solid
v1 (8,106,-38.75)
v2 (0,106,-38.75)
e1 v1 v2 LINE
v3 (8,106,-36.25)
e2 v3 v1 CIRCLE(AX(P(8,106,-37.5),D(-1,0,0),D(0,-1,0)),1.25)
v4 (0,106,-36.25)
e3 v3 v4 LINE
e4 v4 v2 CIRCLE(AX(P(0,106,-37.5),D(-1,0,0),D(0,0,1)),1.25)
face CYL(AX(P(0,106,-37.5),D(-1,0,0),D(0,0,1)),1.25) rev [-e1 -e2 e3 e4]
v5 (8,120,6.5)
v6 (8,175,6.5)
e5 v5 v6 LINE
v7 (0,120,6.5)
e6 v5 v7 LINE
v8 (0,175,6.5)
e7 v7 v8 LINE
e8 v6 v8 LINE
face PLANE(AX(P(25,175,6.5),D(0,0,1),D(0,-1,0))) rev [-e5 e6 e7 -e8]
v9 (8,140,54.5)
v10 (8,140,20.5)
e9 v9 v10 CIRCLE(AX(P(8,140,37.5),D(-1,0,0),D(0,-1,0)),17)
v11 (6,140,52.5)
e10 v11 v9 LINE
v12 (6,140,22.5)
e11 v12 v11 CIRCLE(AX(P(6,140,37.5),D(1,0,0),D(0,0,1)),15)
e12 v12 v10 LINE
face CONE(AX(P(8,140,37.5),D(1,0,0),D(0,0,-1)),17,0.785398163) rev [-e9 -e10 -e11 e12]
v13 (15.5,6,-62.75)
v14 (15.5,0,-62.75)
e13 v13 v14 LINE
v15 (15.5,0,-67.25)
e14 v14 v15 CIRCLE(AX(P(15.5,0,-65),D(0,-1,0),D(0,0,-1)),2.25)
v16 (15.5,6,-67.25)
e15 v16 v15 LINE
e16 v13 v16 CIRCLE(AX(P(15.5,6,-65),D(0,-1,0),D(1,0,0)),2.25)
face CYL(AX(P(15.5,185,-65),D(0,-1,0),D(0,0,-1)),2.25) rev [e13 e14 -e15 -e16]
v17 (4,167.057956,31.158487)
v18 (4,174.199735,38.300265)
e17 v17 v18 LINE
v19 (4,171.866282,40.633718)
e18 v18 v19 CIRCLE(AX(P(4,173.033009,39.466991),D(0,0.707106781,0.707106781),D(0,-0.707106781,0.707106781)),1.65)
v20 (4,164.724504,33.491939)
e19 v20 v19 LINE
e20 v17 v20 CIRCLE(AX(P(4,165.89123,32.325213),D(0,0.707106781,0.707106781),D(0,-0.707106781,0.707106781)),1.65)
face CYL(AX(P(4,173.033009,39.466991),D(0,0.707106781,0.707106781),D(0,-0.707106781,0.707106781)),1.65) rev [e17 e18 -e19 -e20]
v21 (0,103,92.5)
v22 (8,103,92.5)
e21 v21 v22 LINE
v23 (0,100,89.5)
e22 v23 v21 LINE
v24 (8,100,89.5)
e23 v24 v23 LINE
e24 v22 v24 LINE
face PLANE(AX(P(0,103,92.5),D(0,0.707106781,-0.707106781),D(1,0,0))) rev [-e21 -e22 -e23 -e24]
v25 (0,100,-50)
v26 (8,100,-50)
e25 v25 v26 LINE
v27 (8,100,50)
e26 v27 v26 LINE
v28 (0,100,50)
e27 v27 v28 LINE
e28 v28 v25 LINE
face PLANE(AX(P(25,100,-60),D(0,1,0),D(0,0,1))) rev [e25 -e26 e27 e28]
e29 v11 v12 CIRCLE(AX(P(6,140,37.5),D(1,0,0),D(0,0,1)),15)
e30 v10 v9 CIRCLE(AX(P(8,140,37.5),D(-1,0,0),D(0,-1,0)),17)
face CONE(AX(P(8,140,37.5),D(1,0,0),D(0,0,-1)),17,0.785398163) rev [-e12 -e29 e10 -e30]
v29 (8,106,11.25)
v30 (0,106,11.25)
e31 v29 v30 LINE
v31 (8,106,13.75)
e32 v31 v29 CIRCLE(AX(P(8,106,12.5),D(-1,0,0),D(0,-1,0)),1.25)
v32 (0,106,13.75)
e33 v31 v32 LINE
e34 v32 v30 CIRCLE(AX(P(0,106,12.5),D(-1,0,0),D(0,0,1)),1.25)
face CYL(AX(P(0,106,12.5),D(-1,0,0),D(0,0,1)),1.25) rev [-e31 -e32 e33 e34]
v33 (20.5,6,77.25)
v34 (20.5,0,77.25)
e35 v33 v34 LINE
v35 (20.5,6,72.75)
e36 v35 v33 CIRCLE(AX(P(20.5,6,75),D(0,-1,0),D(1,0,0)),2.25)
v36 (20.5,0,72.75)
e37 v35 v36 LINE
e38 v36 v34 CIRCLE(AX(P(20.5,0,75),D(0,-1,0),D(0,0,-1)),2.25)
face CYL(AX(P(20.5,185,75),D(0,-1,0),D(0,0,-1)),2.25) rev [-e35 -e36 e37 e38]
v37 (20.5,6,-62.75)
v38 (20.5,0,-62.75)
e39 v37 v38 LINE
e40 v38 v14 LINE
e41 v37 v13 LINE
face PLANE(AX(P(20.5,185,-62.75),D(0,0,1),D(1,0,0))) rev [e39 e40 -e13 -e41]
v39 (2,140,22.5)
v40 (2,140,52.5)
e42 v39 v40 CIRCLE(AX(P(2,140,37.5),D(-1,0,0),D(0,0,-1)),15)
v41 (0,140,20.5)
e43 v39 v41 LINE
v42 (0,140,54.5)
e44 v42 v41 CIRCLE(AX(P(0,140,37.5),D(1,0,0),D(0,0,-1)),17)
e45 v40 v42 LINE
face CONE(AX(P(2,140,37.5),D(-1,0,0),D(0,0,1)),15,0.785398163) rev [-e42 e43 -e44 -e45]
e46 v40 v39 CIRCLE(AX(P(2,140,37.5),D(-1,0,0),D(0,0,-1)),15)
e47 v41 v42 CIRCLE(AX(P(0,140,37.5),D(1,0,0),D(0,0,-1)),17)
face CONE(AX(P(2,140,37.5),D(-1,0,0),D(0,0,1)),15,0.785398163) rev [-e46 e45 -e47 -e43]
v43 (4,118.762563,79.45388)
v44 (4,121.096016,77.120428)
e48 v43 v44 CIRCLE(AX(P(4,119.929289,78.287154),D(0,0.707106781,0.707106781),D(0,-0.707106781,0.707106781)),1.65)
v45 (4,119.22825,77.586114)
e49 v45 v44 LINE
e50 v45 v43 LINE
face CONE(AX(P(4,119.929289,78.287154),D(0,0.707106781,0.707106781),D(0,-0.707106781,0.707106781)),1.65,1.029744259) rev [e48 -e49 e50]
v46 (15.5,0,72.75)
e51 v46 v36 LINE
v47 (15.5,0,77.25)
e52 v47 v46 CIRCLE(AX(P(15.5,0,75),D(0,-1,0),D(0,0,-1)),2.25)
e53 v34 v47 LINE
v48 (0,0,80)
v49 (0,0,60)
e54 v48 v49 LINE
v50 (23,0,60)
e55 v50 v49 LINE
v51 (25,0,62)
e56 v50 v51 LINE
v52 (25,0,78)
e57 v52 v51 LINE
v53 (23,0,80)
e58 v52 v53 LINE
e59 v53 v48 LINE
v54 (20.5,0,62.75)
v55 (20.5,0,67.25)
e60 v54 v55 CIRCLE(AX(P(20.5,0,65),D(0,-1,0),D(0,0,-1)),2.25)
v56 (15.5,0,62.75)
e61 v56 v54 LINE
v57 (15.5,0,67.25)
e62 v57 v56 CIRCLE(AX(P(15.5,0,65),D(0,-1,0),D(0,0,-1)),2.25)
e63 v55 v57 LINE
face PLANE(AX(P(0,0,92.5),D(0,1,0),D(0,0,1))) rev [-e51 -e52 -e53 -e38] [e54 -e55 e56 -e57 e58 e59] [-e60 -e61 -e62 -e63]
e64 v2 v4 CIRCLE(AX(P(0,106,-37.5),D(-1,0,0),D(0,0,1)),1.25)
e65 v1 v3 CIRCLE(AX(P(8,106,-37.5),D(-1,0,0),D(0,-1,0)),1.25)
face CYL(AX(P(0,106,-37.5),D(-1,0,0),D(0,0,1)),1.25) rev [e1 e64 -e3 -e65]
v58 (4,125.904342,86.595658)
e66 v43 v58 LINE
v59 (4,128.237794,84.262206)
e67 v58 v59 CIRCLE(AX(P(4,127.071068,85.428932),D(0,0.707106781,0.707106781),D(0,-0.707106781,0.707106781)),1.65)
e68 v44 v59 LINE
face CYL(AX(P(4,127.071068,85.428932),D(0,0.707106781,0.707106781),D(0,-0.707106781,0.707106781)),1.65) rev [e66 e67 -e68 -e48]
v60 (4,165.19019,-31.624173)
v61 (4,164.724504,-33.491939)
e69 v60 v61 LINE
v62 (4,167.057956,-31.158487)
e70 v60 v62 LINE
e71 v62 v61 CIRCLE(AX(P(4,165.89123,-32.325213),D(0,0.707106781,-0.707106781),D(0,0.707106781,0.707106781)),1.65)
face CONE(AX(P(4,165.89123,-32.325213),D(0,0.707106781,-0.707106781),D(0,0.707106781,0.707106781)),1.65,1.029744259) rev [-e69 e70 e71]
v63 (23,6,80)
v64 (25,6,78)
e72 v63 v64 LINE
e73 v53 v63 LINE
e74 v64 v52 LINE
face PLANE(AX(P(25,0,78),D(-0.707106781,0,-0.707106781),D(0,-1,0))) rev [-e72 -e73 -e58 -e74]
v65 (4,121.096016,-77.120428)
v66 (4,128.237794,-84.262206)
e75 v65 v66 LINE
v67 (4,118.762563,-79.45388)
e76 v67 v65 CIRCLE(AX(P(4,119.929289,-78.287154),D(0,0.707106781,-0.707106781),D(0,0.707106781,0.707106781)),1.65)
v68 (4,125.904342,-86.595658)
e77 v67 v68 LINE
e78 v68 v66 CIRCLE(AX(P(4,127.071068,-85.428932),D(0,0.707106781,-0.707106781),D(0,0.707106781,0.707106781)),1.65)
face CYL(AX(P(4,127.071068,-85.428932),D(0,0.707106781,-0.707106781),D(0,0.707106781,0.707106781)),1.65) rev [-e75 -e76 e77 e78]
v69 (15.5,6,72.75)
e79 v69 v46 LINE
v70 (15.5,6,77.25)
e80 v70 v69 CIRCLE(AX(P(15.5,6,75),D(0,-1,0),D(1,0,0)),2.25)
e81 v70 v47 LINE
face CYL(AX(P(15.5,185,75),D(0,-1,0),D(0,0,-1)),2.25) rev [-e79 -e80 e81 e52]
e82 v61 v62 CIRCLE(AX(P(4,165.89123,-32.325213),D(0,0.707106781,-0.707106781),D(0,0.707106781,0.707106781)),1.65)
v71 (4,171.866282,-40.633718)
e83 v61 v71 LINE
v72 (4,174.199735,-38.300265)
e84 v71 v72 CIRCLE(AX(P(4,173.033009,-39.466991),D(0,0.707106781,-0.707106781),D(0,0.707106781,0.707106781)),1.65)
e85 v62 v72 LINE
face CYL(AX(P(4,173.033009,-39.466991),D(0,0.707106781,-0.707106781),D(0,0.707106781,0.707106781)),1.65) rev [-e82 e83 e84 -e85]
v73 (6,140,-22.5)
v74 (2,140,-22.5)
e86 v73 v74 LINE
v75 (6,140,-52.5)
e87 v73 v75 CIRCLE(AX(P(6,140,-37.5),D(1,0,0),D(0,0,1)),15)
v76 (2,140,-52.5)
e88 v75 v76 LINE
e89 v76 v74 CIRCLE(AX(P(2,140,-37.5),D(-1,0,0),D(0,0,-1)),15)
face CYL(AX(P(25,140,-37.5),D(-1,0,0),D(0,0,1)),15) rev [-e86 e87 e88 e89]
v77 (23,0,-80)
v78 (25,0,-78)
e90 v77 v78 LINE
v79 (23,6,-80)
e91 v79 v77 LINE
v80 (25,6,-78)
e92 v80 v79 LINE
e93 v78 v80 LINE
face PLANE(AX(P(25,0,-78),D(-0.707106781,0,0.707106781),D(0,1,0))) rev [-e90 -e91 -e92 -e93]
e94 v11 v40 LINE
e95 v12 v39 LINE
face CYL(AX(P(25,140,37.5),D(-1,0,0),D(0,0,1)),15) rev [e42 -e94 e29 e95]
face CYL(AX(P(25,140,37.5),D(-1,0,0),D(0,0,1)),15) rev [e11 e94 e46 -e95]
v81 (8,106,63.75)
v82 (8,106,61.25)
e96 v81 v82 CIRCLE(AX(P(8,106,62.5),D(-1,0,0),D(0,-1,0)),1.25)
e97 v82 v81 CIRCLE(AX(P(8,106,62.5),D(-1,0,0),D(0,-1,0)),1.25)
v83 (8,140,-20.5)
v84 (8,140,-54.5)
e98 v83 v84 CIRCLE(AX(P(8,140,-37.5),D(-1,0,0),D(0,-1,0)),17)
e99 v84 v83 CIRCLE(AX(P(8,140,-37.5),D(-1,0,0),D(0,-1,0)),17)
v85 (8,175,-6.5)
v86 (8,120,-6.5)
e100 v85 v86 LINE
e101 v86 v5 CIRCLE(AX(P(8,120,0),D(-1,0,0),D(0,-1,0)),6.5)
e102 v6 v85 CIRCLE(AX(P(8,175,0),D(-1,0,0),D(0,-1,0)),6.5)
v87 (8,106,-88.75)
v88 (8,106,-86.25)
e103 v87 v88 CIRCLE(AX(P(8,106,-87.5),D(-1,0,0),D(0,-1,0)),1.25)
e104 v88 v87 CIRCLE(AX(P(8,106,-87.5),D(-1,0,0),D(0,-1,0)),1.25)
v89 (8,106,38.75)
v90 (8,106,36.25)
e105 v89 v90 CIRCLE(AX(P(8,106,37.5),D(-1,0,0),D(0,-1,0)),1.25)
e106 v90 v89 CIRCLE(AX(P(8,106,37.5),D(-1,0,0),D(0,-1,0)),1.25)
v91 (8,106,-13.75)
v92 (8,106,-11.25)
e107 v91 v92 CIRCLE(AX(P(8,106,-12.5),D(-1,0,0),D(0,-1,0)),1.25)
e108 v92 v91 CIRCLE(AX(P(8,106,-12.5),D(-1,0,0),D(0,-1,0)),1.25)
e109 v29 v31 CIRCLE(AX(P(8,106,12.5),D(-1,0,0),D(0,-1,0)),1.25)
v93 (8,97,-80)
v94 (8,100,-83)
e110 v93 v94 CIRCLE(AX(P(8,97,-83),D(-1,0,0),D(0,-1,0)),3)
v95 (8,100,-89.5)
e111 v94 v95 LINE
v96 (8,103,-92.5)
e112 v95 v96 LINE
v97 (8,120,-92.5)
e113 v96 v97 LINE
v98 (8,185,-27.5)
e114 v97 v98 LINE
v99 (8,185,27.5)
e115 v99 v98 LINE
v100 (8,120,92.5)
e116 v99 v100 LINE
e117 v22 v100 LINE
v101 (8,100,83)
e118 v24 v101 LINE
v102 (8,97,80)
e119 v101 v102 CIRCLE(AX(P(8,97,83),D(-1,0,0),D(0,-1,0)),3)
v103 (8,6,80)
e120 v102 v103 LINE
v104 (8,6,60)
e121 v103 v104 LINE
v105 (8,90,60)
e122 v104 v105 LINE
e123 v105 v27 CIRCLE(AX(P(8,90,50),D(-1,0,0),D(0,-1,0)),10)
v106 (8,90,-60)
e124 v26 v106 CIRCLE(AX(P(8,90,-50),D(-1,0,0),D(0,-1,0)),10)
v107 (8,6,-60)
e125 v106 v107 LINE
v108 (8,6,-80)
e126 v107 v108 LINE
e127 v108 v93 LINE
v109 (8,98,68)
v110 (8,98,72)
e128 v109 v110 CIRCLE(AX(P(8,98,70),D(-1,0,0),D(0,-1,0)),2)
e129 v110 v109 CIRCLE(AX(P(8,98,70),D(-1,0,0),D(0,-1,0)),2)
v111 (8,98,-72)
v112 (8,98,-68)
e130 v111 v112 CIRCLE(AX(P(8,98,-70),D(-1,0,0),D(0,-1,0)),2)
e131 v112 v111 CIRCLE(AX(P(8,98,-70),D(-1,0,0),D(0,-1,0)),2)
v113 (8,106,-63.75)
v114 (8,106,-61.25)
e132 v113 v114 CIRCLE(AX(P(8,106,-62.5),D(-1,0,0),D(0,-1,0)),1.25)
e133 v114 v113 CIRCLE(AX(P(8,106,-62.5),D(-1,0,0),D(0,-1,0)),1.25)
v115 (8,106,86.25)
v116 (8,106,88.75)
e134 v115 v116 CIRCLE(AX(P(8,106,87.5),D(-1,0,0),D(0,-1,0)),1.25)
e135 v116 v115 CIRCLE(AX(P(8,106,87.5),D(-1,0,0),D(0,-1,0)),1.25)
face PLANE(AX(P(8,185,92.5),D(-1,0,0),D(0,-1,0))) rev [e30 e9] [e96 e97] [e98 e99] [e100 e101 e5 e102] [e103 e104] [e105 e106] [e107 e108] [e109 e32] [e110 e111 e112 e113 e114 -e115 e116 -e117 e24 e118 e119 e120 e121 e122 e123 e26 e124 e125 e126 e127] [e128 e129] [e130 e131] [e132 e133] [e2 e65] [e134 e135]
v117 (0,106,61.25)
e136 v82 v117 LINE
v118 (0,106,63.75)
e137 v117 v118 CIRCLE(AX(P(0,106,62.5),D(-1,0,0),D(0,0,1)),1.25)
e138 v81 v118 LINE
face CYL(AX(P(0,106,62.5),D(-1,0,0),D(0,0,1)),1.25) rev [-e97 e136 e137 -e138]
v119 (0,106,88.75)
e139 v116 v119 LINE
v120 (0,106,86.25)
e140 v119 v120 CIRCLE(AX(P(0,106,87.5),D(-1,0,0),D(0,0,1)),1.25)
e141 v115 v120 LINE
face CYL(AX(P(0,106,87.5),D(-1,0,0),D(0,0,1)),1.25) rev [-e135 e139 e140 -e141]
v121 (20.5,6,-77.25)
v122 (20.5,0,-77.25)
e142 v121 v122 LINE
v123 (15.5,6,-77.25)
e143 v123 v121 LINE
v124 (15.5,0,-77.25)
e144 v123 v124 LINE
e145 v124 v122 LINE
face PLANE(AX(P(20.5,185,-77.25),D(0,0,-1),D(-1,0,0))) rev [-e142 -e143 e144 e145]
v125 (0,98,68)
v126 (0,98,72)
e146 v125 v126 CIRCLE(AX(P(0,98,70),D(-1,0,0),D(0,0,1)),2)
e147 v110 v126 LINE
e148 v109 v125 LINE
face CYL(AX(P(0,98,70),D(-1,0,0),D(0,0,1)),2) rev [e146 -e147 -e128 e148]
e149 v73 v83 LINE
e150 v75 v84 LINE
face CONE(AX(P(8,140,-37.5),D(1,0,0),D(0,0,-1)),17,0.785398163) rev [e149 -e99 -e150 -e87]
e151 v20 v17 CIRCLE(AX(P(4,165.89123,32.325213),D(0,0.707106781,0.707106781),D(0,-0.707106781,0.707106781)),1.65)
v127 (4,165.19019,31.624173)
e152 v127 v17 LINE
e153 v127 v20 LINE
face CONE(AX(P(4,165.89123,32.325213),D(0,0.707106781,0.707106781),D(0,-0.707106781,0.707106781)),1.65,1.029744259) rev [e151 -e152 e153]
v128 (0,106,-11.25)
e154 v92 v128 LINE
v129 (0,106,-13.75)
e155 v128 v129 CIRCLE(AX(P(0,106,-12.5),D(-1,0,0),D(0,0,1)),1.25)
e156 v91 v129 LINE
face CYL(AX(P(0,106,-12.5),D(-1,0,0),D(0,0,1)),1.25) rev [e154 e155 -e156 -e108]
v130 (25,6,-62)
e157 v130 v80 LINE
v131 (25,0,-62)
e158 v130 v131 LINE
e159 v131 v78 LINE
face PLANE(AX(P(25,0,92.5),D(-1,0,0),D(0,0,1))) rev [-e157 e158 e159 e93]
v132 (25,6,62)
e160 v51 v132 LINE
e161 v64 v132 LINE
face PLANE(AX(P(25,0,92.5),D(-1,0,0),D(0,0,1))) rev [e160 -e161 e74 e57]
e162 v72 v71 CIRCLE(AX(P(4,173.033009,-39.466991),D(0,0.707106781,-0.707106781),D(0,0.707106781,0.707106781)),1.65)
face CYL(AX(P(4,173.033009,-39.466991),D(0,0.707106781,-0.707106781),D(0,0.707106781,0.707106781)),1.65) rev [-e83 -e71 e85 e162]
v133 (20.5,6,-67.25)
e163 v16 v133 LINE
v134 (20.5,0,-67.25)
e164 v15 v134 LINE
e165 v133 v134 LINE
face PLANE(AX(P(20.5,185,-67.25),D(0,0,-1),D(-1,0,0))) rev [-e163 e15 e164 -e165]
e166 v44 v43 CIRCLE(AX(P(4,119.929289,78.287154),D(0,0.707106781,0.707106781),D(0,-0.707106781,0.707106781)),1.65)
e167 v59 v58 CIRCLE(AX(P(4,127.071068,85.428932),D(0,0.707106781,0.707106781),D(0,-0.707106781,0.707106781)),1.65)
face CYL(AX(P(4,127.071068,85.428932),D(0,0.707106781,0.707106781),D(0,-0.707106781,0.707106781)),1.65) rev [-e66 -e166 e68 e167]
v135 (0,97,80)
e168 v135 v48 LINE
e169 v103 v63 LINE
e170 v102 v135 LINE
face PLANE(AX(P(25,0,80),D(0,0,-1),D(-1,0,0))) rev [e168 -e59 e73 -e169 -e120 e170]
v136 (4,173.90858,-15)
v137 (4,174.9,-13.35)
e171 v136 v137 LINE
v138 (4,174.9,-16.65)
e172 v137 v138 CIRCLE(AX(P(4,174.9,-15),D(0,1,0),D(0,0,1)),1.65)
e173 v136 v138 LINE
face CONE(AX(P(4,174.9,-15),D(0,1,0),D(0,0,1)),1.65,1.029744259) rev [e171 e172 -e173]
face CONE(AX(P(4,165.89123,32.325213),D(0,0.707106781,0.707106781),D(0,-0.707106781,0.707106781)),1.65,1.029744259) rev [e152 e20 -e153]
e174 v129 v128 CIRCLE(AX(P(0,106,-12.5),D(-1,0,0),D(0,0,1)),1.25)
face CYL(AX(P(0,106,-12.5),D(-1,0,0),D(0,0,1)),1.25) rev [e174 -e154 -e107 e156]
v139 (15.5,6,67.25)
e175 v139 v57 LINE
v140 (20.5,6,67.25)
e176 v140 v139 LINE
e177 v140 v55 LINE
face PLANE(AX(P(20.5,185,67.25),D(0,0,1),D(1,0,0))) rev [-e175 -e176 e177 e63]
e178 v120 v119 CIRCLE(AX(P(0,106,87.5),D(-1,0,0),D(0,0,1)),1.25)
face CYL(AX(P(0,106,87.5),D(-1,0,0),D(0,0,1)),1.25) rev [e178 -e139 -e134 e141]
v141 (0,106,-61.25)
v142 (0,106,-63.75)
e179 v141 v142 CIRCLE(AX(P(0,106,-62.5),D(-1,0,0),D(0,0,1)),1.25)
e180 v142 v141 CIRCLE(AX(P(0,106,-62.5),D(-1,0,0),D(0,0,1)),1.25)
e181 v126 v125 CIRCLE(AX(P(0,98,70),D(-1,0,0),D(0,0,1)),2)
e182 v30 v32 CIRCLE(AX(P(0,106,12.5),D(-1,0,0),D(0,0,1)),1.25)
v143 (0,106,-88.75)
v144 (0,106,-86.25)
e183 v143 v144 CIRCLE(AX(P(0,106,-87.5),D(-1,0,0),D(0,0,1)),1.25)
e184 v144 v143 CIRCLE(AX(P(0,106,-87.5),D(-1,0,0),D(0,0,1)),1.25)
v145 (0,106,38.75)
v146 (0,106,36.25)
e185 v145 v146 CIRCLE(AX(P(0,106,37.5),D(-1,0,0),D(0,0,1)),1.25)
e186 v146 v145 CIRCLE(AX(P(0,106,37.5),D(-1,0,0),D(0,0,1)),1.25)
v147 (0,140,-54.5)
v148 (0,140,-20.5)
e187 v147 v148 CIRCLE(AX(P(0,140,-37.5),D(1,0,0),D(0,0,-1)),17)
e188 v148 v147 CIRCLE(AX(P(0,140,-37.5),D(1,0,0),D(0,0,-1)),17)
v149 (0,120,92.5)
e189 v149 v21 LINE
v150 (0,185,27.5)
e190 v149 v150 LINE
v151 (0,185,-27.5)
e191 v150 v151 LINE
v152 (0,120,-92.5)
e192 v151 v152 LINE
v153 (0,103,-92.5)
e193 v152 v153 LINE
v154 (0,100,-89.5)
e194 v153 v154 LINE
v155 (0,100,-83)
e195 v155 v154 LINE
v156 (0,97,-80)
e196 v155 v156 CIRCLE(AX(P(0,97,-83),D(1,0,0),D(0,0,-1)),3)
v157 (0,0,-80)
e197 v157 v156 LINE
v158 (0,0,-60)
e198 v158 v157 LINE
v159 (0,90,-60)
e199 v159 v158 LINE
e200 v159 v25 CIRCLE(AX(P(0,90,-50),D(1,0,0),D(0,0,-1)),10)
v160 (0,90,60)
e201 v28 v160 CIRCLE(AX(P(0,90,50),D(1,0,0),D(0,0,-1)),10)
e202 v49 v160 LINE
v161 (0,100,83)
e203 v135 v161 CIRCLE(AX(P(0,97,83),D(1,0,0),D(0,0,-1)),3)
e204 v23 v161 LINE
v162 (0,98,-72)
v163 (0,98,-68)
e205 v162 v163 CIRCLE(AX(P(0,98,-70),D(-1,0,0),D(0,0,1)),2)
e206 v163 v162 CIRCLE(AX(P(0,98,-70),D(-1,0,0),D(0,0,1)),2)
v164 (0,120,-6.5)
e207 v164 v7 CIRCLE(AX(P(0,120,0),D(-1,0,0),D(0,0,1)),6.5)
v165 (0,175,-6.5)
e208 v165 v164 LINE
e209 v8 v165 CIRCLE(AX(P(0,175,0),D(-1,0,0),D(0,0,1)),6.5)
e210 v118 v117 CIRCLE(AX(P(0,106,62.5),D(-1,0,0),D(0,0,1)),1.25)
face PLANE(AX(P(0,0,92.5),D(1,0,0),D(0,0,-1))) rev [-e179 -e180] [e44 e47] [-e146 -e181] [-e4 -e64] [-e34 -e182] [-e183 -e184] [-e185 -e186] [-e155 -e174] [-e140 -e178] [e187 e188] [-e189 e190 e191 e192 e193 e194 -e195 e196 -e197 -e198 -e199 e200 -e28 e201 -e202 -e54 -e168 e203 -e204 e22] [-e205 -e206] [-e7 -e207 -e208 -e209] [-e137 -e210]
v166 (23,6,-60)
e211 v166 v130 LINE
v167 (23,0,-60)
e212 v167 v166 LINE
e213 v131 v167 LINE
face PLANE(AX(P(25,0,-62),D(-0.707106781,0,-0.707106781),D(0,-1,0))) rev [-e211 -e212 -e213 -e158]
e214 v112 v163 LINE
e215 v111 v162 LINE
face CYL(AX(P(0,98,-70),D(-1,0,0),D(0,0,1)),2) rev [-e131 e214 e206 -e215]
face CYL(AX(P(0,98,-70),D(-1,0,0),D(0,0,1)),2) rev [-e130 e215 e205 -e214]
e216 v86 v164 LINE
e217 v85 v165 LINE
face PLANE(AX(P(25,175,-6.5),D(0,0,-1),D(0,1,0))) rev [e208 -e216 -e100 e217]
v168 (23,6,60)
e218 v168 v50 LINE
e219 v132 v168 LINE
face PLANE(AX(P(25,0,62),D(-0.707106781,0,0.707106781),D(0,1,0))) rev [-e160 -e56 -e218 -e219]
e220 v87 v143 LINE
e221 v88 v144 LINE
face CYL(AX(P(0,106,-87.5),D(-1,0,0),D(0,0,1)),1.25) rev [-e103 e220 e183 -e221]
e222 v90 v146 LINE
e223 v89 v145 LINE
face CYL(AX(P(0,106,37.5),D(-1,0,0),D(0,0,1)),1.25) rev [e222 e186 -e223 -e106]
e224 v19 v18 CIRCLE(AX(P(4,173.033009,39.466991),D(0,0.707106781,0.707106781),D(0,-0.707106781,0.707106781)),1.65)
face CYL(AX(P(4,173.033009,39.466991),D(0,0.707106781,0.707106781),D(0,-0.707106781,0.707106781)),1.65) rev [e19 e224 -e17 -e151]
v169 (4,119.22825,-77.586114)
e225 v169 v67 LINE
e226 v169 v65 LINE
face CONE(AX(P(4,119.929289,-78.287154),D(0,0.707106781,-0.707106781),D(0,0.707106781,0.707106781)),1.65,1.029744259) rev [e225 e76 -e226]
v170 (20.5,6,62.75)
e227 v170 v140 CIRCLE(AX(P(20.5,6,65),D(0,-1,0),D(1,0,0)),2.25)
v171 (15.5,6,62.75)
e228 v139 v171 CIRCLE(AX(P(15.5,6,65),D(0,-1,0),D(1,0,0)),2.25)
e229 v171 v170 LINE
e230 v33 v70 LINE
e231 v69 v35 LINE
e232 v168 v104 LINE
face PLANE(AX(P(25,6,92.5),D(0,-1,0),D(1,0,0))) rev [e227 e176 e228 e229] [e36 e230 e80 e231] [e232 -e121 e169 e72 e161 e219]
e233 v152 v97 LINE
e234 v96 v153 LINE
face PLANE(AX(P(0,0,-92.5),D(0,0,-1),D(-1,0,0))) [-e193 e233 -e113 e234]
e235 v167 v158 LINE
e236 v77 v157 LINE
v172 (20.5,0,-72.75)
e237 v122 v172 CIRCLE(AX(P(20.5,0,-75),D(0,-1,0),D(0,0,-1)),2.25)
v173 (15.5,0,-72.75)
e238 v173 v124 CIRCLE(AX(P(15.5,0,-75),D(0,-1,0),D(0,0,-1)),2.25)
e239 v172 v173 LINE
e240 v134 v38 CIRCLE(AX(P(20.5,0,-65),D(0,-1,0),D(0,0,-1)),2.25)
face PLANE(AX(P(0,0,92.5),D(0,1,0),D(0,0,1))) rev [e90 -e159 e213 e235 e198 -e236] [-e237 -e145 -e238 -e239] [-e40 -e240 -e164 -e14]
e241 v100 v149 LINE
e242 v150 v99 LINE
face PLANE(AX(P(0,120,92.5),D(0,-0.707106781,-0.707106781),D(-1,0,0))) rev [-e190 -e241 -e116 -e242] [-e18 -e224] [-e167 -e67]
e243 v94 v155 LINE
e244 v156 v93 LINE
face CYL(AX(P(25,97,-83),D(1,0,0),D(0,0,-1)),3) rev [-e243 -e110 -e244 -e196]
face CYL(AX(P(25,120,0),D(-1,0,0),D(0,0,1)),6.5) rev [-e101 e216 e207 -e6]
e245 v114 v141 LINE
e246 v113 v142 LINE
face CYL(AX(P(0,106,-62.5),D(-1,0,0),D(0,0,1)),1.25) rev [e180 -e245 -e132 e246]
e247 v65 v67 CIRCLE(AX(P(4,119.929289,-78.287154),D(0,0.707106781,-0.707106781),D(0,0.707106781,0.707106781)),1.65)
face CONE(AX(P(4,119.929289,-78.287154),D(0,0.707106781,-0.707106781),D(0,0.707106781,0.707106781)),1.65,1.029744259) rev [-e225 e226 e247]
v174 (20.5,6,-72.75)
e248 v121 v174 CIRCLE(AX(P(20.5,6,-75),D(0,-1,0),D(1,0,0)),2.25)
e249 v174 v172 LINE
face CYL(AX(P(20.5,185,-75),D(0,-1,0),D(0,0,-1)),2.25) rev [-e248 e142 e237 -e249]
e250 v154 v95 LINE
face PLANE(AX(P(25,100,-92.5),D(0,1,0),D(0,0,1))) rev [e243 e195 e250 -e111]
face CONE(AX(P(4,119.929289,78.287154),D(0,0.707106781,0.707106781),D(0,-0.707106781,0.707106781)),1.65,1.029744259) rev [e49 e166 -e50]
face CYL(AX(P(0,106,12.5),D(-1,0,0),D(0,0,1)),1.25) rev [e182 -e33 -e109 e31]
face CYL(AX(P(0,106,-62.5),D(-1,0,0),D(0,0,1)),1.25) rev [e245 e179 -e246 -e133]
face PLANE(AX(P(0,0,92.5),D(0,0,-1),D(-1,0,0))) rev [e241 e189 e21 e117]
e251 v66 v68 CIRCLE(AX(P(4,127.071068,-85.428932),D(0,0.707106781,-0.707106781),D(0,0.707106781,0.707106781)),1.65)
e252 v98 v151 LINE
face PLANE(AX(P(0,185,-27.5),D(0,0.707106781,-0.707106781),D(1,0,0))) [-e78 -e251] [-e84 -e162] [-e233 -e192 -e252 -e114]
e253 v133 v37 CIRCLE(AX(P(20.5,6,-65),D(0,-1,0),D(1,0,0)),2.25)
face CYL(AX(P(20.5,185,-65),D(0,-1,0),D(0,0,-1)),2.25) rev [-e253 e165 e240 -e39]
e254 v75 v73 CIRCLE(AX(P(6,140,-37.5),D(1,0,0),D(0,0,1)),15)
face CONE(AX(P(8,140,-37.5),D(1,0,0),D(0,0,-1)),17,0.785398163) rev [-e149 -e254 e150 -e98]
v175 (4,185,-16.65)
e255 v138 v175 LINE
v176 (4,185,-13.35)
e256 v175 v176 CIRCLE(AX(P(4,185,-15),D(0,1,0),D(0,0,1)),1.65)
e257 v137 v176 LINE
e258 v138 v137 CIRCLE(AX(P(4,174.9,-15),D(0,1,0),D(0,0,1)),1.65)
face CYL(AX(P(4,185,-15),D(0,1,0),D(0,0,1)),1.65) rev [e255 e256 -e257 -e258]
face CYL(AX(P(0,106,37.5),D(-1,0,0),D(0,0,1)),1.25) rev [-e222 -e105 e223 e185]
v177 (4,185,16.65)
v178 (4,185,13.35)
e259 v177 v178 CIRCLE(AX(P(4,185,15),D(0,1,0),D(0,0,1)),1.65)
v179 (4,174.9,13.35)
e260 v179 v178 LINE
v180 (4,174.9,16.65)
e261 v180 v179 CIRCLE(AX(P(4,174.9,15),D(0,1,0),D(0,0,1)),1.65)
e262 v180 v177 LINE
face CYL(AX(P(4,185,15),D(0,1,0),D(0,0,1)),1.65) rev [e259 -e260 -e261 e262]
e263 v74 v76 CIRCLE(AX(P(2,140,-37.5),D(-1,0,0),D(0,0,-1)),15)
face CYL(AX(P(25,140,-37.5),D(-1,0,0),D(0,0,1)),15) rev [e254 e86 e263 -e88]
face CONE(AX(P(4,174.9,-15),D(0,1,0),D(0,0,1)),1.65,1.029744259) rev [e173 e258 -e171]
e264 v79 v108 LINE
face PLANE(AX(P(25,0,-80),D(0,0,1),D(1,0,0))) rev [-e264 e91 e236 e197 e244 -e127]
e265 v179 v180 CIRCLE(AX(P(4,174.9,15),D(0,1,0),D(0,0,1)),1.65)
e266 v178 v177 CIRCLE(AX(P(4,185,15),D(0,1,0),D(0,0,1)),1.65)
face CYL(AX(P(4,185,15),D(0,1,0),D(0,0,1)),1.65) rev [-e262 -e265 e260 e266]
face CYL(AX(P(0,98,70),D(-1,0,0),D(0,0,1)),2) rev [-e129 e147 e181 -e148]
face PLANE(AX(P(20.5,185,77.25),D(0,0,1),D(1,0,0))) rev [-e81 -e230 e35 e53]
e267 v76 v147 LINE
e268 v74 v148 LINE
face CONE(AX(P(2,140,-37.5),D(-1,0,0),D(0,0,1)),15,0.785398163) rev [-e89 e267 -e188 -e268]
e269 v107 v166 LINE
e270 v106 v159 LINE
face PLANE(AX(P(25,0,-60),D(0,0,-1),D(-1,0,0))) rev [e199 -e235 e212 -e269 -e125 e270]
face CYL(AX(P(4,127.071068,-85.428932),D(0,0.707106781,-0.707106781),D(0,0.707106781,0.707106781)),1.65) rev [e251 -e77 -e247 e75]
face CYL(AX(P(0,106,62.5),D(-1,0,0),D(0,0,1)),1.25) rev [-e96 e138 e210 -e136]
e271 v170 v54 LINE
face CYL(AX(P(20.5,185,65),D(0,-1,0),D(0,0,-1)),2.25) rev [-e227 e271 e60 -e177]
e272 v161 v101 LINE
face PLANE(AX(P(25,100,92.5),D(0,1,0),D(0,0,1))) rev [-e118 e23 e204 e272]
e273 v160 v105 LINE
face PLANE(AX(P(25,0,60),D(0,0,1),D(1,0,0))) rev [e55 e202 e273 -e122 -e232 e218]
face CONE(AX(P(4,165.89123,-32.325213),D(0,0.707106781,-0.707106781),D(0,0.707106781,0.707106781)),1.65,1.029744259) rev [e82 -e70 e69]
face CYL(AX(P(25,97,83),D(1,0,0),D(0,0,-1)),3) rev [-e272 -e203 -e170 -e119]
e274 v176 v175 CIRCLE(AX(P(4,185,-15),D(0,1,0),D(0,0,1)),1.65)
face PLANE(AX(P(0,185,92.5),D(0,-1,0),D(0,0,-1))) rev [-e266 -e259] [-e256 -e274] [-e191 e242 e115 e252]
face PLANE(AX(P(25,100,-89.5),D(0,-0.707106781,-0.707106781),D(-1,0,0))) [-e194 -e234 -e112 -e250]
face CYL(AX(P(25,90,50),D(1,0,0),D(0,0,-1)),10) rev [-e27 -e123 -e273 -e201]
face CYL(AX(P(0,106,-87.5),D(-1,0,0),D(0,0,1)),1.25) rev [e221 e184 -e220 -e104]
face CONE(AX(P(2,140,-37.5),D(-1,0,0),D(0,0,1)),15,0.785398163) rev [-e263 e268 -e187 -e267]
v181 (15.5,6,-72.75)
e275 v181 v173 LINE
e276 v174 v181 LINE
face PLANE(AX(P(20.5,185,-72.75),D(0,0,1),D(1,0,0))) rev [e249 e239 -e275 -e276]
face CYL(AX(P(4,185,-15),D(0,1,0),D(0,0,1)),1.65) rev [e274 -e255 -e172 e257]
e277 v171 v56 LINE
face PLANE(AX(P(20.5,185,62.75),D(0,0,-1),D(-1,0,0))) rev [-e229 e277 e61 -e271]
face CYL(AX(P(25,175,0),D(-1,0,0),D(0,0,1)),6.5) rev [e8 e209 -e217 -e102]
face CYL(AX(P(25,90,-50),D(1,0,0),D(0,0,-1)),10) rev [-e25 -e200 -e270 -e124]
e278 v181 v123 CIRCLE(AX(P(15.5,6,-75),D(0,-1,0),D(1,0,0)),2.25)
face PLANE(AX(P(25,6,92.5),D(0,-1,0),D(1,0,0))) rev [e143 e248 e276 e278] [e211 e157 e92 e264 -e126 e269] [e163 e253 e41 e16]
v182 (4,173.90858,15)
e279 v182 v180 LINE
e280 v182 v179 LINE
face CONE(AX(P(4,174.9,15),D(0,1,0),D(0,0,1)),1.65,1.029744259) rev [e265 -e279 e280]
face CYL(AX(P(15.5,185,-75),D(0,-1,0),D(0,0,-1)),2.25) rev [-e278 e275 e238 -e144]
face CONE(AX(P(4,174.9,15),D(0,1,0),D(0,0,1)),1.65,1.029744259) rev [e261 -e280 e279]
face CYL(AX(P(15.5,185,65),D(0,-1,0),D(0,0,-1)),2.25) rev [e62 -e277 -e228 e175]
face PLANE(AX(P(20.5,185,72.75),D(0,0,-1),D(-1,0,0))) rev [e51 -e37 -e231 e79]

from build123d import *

# Parameters (mm, degrees)
BOSS_EXTRUDE1_DEPTH        = 92.5
CUT_EXTRUDE5_DEPTH         = 209.3416665
M4_TAPPED_HOLE1_D          = 3.3
M4_TAPPED_HOLE1_DEPTH      = 10.1
M4_TAPPED_HOLE1_TIP        = 0.991420021
SKETCH19_W                 = 12.5
SKETCH19_H                 = 100
CUT_EXTRUDE6_DEPTH         = 209.3416665
SKETCH10_R                 = 15
SKETCH10_W                 = 120
SKETCH10_H                 = 100
CUT_EXTRUDE3_DEPTH         = 209.3416665
M3_TAPPED_HOLE1_D          = 2.5
SIZE_MM_BLIND_PIN_HOLE1_D  = 4
CUT_EXTRUDE7_DEPTH         = 209.3416665
CHAMFER2_SIZE              = 65
CHAMFER3_SIZE              = 3
CHAMFER4_SIZE              = 2
FILLET1_R                  = 10
FILLET2_R                  = 3
M4_TAPPED_HOLE2_AT_2_COUNT = 2
M4_TAPPED_HOLE2_AT_2_PITCH = 65


with BuildPart() as part:
    # Sketch1 → Boss-Extrude1 (new, symmetric)
    with BuildSketch(Plane.XY):
        Polygon((0, 0), (25, 0), (25, 6), (8, 6), (8, 185), (0, 185), align=None)
    extrude(amount=BOSS_EXTRUDE1_DEPTH, both=True)

    # Sketch16 → Cut-Extrude5 (cut, through all)
    with BuildSketch(Plane.ZY):
        with BuildLine():
            Line((6.5, 175), (6.5, 120))
            ThreePointArc((6.5, 120), (0, 113.5), (-6.5, 120))
            Line((-6.5, 120), (-6.5, 175))
            ThreePointArc((-6.5, 175), (0, 181.5), (6.5, 175))
        make_face()
    extrude(amount=-CUT_EXTRUDE5_DEPTH, mode=Mode.SUBTRACT)

    # M4 Tapped Hole1
    with Locations(Plane(origin=(0, 185, 0), x_dir=(1, 0, 0), z_dir=(0, 1, 0))):
        with Locations((4, 15), (4, -15)):
            Hole(M4_TAPPED_HOLE1_D / 2, depth=M4_TAPPED_HOLE1_DEPTH)
            with Locations((0, 0, -(M4_TAPPED_HOLE1_DEPTH + M4_TAPPED_HOLE1_TIP / 2))):  # 118° drill point
                Cone(0, M4_TAPPED_HOLE1_D / 2, M4_TAPPED_HOLE1_TIP, mode=Mode.SUBTRACT)

    # Sketch19 → Cut-Extrude6 (cut, through all)
    with BuildSketch(Plane.ZY):
        with Locations((86.25, 50)):
            Rectangle(SKETCH19_W, SKETCH19_H)
        with Locations((-86.25, 50)):
            Rectangle(SKETCH19_W, SKETCH19_H)
    extrude(amount=-CUT_EXTRUDE6_DEPTH, mode=Mode.SUBTRACT)

    # Sketch10 → Cut-Extrude3 (cut, through all)
    with BuildSketch(Plane.ZY):
        with Locations((37.5, 140)):
            Circle(SKETCH10_R)
        with Locations((-37.5, 140)):
            Circle(SKETCH10_R)
        with Locations((0, 50)):
            Rectangle(SKETCH10_W, SKETCH10_H)
    extrude(amount=-CUT_EXTRUDE3_DEPTH, mode=Mode.SUBTRACT)

    # M3 Tapped Hole1 (through all)
    with Locations(Plane.ZY):
        with Locations((-87.5, 106), (-62.5, 106), (-37.5, 106), (-12.5, 106), (12.5, 106), (37.5, 106), (62.5, 106), (87.5, 106)):
            Hole(M3_TAPPED_HOLE1_D / 2)

    # Size mm Blind Pin Hole1 (through all)
    with Locations(Plane.ZY):
        with Locations((-70, 98), (70, 98)):
            Hole(SIZE_MM_BLIND_PIN_HOLE1_D / 2)

    # Sketch25 → Cut-Extrude7 (cut, through all)
    with BuildSketch(Plane.XZ):
        with BuildLine():
            Line((20.5, 72.75), (15.5, 72.75))
            ThreePointArc((15.5, 72.75), (13.25, 75), (15.5, 77.25))
            Line((15.5, 77.25), (20.5, 77.25))
            ThreePointArc((20.5, 77.25), (22.75, 75), (20.5, 72.75))
        make_face()
        with BuildLine():
            Line((20.5, 62.75), (15.5, 62.75))
            ThreePointArc((15.5, 62.75), (13.25, 65), (15.5, 67.25))
            Line((15.5, 67.25), (20.5, 67.25))
            ThreePointArc((20.5, 67.25), (22.75, 65), (20.5, 62.75))
        make_face()
        with BuildLine():
            Line((20.5, -67.25), (15.5, -67.25))
            ThreePointArc((15.5, -67.25), (13.25, -65), (15.5, -62.75))
            Line((15.5, -62.75), (20.5, -62.75))
            ThreePointArc((20.5, -62.75), (22.75, -65), (20.5, -67.25))
        make_face()
        with BuildLine():
            Line((20.5, -77.25), (15.5, -77.25))
            ThreePointArc((15.5, -77.25), (13.25, -75), (15.5, -72.75))
            Line((15.5, -72.75), (20.5, -72.75))
            ThreePointArc((20.5, -72.75), (22.75, -75), (20.5, -77.25))
        make_face()
    extrude(amount=-CUT_EXTRUDE7_DEPTH, mode=Mode.SUBTRACT)

    # Chamfer2
    chamfer2_edges = [part.edges().sort_by_distance(p)[0] for p in [
        (4, 185, 92.5),
        (4, 185, -92.5),
    ]]
    chamfer(chamfer2_edges, length=CHAMFER2_SIZE)

    # Chamfer3
    chamfer3_edges = [part.edges().sort_by_distance(p)[0] for p in [
        (4, 100, 92.5),
        (4, 100, -92.5),
    ]]
    chamfer(chamfer3_edges, length=CHAMFER3_SIZE)

    # Chamfer4
    chamfer4_edges = [part.edges().sort_by_distance(p)[0] for p in [
        (8, 140, 22.5),
        (0, 140, 22.5),
        (8, 140, -52.5),
        (0, 140, -52.5),
        (25, 3, 80),
        (25, 3, -80),
        (25, 3, -60),
        (25, 3, 60),
    ]]
    chamfer(chamfer4_edges, length=CHAMFER4_SIZE)

    # Fillet1
    fillet1_edges = [part.edges().sort_by_distance(p)[0] for p in [
        (4, 100, -60),
        (4, 100, 60),
    ]]
    fillet(fillet1_edges, radius=FILLET1_R)

    # Fillet2
    fillet2_edges = [part.edges().sort_by_distance(p)[0] for p in [
        (4, 100, 80),
        (4, 100, -80),
    ]]
    fillet(fillet2_edges, radius=FILLET2_R)

    # Sketch26 → M4 Tapped Hole2 (revolve, cut)
    with BuildSketch(Plane(origin=(4, 173.033008589, -39.466991411), x_dir=(0, 0.7071067811865487, 0.7071067811865465), z_dir=(1, 0, 0))):
        Polygon((0, 0), (0, 11.091420021), (1.65, 10.1), (1.65, 0), align=None)
    m4_tapped_hole2 = revolve(axis=Axis((4, 177.52313665, -43.957119472), (0, -0.7071067811865465, 0.7071067811865486)), mode=Mode.SUBTRACT)

    # M4 Tapped Hole2 at 2: M4 Tapped Hole2 ×2
    with Locations(*[Vector(0, -0.7071067811865485, -0.7071067811865466) * (i * M4_TAPPED_HOLE2_AT_2_PITCH) for i in range(1, M4_TAPPED_HOLE2_AT_2_COUNT)]):
        add(m4_tapped_hole2, mode=Mode.SUBTRACT)

    # Mirror1: M4 Tapped Hole2 across plane
    add(m4_tapped_hole2.mirror(Plane.XY), mode=Mode.SUBTRACT)

    # Mirror1 copy 1 sketch → Mirror1 copy 1 (revolve, cut)
    with BuildSketch(Plane(origin=(4, 127.071067812, 85.428932188), x_dir=(0, 0.7071067811865487, -0.7071067811865465), z_dir=(1, 0, 0))):
        Polygon((0, 0), (0, -11.091420021), (1.65, -10.1), (1.65, 0), align=None)
    revolve(axis=Axis((4, 131.561195872, 89.919060249), (0, 0.7071067811865465, 0.7071067811865486)), mode=Mode.SUBTRACT)


solid = part.part
